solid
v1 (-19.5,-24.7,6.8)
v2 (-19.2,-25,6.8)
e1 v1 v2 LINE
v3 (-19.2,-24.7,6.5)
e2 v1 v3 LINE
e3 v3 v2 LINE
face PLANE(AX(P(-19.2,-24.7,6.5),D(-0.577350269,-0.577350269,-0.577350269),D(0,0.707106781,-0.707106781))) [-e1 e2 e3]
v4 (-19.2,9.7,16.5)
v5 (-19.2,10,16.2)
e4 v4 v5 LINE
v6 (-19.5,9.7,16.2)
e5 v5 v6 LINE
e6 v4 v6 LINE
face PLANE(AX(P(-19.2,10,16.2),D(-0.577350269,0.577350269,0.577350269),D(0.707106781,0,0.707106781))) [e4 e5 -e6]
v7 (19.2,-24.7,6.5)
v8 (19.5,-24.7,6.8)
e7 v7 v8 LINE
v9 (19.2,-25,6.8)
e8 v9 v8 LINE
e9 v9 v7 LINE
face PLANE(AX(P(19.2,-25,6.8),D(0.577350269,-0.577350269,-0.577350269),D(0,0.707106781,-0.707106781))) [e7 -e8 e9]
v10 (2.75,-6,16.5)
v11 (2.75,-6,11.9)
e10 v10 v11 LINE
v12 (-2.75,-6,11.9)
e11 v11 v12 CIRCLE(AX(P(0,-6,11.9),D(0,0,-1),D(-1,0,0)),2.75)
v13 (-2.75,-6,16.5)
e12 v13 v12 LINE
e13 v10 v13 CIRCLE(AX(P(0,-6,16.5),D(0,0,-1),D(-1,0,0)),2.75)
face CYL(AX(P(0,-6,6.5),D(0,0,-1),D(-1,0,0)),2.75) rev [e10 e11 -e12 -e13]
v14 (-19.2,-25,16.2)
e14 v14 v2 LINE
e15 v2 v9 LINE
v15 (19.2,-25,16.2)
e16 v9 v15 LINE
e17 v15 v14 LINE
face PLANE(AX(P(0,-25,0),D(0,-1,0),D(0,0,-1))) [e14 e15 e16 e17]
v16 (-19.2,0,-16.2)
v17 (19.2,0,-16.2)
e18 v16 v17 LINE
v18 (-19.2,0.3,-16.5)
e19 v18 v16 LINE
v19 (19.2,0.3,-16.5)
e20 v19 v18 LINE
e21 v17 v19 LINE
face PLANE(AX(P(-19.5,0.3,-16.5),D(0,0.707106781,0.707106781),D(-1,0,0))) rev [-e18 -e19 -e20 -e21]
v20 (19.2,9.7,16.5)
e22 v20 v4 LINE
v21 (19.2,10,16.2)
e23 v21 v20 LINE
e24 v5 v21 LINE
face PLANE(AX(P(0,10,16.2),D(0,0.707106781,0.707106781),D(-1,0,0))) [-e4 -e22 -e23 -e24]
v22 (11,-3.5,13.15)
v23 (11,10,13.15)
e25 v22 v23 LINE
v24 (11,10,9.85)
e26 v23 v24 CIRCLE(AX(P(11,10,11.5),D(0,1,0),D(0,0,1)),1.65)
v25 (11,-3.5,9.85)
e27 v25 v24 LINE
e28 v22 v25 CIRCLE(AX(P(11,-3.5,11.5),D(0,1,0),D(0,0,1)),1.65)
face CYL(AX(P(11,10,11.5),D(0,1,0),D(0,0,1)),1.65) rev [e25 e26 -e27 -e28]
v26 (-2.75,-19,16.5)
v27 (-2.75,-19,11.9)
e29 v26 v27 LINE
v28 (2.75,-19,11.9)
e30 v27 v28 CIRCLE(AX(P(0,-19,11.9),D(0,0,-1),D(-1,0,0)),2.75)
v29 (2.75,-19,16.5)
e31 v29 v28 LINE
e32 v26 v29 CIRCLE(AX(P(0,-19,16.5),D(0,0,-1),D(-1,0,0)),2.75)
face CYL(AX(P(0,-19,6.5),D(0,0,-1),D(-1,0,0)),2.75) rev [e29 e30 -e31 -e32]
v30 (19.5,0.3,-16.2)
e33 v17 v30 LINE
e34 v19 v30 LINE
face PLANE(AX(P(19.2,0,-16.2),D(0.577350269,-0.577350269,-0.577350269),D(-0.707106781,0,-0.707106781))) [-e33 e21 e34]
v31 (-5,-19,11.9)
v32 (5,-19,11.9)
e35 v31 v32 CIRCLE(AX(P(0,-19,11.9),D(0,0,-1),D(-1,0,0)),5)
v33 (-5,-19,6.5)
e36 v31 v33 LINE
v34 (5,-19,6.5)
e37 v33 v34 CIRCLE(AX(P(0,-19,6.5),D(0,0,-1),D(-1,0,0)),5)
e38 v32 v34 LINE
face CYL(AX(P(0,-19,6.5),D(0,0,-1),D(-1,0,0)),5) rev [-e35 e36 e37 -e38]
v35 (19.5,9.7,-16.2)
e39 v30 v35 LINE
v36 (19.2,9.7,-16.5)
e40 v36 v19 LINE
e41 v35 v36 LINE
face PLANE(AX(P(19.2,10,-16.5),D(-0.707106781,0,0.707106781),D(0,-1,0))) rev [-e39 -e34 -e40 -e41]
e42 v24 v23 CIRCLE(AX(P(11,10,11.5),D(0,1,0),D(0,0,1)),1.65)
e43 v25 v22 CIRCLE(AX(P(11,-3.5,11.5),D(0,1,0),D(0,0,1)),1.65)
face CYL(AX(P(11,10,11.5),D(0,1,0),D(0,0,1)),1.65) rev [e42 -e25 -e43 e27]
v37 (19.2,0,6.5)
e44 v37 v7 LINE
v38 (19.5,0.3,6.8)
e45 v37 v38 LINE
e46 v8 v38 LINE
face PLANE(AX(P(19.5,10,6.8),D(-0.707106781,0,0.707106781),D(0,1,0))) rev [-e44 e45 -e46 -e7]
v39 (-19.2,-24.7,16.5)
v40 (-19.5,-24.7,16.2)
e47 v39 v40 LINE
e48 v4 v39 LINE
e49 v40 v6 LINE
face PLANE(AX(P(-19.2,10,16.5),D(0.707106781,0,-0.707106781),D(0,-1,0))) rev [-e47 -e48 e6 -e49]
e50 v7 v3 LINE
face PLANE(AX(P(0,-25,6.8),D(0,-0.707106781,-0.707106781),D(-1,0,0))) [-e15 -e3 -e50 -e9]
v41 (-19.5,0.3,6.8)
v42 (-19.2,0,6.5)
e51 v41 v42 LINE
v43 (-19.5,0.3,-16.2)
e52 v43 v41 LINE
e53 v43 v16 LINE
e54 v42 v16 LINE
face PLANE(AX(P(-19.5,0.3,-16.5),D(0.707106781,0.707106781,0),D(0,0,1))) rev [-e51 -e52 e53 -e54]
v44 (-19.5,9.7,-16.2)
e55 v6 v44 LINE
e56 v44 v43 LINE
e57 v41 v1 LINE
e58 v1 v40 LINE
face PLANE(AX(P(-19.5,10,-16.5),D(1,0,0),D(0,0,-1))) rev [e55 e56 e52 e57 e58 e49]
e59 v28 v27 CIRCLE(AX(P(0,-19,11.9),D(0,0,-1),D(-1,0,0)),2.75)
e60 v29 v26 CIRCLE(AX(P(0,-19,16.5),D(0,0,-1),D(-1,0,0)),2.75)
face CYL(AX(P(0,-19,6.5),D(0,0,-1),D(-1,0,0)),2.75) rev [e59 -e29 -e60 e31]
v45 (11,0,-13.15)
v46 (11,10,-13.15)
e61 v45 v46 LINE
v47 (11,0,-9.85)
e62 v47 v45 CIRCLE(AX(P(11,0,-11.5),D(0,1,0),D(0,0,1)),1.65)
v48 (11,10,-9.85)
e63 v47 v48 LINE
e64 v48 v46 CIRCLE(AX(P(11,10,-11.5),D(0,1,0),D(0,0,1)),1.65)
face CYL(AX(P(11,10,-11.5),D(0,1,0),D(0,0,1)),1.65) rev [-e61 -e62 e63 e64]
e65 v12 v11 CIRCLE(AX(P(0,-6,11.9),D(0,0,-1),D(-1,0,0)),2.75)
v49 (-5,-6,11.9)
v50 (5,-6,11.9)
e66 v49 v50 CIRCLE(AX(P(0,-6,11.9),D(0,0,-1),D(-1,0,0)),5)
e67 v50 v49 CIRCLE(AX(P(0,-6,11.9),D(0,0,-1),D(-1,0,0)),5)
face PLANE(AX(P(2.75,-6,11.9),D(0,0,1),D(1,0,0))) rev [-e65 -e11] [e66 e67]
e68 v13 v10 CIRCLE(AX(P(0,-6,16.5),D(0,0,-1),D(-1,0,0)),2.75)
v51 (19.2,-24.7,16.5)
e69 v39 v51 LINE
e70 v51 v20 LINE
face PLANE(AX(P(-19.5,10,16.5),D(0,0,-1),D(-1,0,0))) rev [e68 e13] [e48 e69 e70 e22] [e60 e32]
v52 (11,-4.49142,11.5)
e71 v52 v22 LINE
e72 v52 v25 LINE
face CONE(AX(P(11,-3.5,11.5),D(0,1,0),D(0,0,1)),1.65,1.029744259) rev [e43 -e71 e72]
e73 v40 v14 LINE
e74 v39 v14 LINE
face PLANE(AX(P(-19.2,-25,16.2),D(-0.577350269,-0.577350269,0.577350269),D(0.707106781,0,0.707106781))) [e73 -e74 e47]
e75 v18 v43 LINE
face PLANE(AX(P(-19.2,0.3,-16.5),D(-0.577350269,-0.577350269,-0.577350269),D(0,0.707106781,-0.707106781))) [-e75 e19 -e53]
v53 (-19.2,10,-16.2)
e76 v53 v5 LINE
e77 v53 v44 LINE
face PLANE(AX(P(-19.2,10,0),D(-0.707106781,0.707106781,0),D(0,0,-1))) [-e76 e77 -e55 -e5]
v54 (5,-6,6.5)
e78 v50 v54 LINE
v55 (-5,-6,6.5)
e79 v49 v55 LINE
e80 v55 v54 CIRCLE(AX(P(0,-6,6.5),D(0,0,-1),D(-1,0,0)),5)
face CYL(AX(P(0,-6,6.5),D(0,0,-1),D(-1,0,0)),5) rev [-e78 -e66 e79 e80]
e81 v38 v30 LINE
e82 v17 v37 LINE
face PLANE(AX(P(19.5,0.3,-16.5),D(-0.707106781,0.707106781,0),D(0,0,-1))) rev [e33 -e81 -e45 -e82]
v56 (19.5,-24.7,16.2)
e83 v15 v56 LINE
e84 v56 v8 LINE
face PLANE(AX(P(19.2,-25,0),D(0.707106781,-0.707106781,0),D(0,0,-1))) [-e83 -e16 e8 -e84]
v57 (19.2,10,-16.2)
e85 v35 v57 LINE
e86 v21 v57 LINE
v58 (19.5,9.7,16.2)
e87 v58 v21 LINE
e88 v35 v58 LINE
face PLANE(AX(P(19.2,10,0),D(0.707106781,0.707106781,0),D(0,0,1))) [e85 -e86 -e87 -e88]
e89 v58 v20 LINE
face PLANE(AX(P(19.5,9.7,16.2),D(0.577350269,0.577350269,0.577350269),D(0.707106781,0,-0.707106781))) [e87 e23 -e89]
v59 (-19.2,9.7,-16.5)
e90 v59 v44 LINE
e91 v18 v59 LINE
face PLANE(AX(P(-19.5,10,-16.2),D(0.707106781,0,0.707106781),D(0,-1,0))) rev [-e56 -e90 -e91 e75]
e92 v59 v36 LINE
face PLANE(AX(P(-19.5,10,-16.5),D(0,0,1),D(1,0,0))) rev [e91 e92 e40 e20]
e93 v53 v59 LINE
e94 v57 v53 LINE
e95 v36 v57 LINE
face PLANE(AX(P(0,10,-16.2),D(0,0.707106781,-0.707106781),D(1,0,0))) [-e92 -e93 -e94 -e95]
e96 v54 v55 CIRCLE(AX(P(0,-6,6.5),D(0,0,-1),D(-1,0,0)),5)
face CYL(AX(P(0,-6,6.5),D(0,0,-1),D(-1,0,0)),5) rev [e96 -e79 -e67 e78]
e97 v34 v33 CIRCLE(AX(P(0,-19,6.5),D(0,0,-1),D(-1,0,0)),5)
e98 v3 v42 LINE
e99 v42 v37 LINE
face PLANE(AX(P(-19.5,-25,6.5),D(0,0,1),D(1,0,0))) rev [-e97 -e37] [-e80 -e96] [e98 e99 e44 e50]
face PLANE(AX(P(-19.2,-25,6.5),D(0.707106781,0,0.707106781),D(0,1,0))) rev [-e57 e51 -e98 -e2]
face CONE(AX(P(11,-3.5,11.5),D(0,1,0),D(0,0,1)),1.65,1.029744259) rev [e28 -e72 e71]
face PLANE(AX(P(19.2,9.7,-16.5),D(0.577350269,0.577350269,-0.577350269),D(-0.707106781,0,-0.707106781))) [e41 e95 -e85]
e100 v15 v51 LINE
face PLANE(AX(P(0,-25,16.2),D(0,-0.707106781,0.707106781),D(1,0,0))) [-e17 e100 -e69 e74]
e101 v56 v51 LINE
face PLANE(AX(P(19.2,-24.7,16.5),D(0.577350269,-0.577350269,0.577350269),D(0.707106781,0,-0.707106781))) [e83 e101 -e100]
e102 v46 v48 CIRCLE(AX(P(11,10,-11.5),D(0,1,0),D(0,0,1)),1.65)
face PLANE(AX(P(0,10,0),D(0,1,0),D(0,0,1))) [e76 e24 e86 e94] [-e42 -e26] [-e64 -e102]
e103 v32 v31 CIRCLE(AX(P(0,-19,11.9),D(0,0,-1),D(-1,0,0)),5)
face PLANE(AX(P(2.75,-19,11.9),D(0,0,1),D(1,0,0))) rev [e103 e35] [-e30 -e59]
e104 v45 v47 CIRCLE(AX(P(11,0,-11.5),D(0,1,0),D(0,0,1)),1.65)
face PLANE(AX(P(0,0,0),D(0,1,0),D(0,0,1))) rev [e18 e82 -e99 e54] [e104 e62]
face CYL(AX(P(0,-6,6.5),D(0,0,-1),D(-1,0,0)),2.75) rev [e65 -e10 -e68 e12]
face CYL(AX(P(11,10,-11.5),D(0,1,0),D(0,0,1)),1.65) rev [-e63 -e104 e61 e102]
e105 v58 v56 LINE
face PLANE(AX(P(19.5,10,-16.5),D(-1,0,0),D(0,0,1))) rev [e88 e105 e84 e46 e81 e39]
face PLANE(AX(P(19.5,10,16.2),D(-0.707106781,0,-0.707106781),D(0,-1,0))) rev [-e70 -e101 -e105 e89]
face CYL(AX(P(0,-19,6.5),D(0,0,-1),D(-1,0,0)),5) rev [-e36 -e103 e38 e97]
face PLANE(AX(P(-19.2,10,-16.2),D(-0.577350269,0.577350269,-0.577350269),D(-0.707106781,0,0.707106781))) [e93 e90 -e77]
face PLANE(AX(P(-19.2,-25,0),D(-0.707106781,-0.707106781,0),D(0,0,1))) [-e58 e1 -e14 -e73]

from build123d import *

# Parameters (mm, degrees)
SKETCH_1_W                   = 39
SKETCH_1_H                   = 33
EXTRUDE_1_DEPTH              = 10
SKETCH_2_W                   = 39
SKETCH_2_H                   = 10
EXTRUDE_2_DEPTH              = 25
HOLE_WIZARD_M4_1_D           = 3.3
HOLE_WIZARD_M4_1_DEPTH       = 13.5
HOLE_WIZARD_M4_1_TIP         = 0.991420021
HOLE_WIZARD_M5_1_D           = 5.5
HOLE_WIZARD_M5_1_CBORE_D     = 10
HOLE_WIZARD_M5_1_CBORE_DEPTH = 5.4
CHAMFER_1_SIZE               = 0.3


with BuildPart() as part:
    # 草图1 → 凸台-拉伸1 (new body)
    with BuildSketch(Plane(origin=(0, 0, 0), x_dir=(1, 0, 0), z_dir=(0, 1, 0))):
        Rectangle(SKETCH_1_W, SKETCH_1_H)
    extrude(amount=EXTRUDE_1_DEPTH)

    # 草图2 → 凸台-拉伸2 (add)
    with BuildSketch(Plane.XZ):
        with Locations((0, 11.5)):
            Rectangle(SKETCH_2_W, SKETCH_2_H)
    extrude(amount=EXTRUDE_2_DEPTH)

    # M4 螺纹孔1
    with Locations(Plane(origin=(0, 10, 0), x_dir=(1, 0, 0), z_dir=(0, 1, 0))):
        with Locations((11, 11.5), (11, -11.5)):
            Hole(HOLE_WIZARD_M4_1_D / 2, depth=HOLE_WIZARD_M4_1_DEPTH)
            with Locations((0, 0, -(HOLE_WIZARD_M4_1_DEPTH + HOLE_WIZARD_M4_1_TIP / 2))):  # 118° drill point
                Cone(0, HOLE_WIZARD_M4_1_D / 2, HOLE_WIZARD_M4_1_TIP, mode=Mode.SUBTRACT)

    # M5 六角凹头螺钉的柱形沉头孔1 (through all)
    with Locations(Plane(origin=(0, 0, 6.5), x_dir=(-1, 0, 0), z_dir=(0, 0, -1))):
        with Locations((0, -6), (0, -19)):
            CounterBoreHole(HOLE_WIZARD_M5_1_D / 2, HOLE_WIZARD_M5_1_CBORE_D / 2, HOLE_WIZARD_M5_1_CBORE_DEPTH)

    # 倒角1
    chamfer_1_edges = [part.edges().sort_by_distance(p)[0] for p in [
        (0, -25, 16.5),
        (0, -25, 6.5),
        (0, 10, -16.5),
        (0, 0, -16.5),
        (-19.5, 5, -16.5),
        (-19.5, 10, 0),
        (-19.5, 0, -5),
        (-19.5, -12.5, 6.5),
        (-19.5, -25, 11.5),
        (-19.5, -7.5, 16.5),
        (19.5, 10, 0),
        (19.5, 5, -16.5),
        (19.5, 0, -5),
        (19.5, -12.5, 6.5),
        (19.5, -25, 11.5),
        (19.5, -7.5, 16.5),
        (0, 10, 16.5),
    ]]
    chamfer(chamfer_1_edges, length=CHAMFER_1_SIZE)


solid = part.part
